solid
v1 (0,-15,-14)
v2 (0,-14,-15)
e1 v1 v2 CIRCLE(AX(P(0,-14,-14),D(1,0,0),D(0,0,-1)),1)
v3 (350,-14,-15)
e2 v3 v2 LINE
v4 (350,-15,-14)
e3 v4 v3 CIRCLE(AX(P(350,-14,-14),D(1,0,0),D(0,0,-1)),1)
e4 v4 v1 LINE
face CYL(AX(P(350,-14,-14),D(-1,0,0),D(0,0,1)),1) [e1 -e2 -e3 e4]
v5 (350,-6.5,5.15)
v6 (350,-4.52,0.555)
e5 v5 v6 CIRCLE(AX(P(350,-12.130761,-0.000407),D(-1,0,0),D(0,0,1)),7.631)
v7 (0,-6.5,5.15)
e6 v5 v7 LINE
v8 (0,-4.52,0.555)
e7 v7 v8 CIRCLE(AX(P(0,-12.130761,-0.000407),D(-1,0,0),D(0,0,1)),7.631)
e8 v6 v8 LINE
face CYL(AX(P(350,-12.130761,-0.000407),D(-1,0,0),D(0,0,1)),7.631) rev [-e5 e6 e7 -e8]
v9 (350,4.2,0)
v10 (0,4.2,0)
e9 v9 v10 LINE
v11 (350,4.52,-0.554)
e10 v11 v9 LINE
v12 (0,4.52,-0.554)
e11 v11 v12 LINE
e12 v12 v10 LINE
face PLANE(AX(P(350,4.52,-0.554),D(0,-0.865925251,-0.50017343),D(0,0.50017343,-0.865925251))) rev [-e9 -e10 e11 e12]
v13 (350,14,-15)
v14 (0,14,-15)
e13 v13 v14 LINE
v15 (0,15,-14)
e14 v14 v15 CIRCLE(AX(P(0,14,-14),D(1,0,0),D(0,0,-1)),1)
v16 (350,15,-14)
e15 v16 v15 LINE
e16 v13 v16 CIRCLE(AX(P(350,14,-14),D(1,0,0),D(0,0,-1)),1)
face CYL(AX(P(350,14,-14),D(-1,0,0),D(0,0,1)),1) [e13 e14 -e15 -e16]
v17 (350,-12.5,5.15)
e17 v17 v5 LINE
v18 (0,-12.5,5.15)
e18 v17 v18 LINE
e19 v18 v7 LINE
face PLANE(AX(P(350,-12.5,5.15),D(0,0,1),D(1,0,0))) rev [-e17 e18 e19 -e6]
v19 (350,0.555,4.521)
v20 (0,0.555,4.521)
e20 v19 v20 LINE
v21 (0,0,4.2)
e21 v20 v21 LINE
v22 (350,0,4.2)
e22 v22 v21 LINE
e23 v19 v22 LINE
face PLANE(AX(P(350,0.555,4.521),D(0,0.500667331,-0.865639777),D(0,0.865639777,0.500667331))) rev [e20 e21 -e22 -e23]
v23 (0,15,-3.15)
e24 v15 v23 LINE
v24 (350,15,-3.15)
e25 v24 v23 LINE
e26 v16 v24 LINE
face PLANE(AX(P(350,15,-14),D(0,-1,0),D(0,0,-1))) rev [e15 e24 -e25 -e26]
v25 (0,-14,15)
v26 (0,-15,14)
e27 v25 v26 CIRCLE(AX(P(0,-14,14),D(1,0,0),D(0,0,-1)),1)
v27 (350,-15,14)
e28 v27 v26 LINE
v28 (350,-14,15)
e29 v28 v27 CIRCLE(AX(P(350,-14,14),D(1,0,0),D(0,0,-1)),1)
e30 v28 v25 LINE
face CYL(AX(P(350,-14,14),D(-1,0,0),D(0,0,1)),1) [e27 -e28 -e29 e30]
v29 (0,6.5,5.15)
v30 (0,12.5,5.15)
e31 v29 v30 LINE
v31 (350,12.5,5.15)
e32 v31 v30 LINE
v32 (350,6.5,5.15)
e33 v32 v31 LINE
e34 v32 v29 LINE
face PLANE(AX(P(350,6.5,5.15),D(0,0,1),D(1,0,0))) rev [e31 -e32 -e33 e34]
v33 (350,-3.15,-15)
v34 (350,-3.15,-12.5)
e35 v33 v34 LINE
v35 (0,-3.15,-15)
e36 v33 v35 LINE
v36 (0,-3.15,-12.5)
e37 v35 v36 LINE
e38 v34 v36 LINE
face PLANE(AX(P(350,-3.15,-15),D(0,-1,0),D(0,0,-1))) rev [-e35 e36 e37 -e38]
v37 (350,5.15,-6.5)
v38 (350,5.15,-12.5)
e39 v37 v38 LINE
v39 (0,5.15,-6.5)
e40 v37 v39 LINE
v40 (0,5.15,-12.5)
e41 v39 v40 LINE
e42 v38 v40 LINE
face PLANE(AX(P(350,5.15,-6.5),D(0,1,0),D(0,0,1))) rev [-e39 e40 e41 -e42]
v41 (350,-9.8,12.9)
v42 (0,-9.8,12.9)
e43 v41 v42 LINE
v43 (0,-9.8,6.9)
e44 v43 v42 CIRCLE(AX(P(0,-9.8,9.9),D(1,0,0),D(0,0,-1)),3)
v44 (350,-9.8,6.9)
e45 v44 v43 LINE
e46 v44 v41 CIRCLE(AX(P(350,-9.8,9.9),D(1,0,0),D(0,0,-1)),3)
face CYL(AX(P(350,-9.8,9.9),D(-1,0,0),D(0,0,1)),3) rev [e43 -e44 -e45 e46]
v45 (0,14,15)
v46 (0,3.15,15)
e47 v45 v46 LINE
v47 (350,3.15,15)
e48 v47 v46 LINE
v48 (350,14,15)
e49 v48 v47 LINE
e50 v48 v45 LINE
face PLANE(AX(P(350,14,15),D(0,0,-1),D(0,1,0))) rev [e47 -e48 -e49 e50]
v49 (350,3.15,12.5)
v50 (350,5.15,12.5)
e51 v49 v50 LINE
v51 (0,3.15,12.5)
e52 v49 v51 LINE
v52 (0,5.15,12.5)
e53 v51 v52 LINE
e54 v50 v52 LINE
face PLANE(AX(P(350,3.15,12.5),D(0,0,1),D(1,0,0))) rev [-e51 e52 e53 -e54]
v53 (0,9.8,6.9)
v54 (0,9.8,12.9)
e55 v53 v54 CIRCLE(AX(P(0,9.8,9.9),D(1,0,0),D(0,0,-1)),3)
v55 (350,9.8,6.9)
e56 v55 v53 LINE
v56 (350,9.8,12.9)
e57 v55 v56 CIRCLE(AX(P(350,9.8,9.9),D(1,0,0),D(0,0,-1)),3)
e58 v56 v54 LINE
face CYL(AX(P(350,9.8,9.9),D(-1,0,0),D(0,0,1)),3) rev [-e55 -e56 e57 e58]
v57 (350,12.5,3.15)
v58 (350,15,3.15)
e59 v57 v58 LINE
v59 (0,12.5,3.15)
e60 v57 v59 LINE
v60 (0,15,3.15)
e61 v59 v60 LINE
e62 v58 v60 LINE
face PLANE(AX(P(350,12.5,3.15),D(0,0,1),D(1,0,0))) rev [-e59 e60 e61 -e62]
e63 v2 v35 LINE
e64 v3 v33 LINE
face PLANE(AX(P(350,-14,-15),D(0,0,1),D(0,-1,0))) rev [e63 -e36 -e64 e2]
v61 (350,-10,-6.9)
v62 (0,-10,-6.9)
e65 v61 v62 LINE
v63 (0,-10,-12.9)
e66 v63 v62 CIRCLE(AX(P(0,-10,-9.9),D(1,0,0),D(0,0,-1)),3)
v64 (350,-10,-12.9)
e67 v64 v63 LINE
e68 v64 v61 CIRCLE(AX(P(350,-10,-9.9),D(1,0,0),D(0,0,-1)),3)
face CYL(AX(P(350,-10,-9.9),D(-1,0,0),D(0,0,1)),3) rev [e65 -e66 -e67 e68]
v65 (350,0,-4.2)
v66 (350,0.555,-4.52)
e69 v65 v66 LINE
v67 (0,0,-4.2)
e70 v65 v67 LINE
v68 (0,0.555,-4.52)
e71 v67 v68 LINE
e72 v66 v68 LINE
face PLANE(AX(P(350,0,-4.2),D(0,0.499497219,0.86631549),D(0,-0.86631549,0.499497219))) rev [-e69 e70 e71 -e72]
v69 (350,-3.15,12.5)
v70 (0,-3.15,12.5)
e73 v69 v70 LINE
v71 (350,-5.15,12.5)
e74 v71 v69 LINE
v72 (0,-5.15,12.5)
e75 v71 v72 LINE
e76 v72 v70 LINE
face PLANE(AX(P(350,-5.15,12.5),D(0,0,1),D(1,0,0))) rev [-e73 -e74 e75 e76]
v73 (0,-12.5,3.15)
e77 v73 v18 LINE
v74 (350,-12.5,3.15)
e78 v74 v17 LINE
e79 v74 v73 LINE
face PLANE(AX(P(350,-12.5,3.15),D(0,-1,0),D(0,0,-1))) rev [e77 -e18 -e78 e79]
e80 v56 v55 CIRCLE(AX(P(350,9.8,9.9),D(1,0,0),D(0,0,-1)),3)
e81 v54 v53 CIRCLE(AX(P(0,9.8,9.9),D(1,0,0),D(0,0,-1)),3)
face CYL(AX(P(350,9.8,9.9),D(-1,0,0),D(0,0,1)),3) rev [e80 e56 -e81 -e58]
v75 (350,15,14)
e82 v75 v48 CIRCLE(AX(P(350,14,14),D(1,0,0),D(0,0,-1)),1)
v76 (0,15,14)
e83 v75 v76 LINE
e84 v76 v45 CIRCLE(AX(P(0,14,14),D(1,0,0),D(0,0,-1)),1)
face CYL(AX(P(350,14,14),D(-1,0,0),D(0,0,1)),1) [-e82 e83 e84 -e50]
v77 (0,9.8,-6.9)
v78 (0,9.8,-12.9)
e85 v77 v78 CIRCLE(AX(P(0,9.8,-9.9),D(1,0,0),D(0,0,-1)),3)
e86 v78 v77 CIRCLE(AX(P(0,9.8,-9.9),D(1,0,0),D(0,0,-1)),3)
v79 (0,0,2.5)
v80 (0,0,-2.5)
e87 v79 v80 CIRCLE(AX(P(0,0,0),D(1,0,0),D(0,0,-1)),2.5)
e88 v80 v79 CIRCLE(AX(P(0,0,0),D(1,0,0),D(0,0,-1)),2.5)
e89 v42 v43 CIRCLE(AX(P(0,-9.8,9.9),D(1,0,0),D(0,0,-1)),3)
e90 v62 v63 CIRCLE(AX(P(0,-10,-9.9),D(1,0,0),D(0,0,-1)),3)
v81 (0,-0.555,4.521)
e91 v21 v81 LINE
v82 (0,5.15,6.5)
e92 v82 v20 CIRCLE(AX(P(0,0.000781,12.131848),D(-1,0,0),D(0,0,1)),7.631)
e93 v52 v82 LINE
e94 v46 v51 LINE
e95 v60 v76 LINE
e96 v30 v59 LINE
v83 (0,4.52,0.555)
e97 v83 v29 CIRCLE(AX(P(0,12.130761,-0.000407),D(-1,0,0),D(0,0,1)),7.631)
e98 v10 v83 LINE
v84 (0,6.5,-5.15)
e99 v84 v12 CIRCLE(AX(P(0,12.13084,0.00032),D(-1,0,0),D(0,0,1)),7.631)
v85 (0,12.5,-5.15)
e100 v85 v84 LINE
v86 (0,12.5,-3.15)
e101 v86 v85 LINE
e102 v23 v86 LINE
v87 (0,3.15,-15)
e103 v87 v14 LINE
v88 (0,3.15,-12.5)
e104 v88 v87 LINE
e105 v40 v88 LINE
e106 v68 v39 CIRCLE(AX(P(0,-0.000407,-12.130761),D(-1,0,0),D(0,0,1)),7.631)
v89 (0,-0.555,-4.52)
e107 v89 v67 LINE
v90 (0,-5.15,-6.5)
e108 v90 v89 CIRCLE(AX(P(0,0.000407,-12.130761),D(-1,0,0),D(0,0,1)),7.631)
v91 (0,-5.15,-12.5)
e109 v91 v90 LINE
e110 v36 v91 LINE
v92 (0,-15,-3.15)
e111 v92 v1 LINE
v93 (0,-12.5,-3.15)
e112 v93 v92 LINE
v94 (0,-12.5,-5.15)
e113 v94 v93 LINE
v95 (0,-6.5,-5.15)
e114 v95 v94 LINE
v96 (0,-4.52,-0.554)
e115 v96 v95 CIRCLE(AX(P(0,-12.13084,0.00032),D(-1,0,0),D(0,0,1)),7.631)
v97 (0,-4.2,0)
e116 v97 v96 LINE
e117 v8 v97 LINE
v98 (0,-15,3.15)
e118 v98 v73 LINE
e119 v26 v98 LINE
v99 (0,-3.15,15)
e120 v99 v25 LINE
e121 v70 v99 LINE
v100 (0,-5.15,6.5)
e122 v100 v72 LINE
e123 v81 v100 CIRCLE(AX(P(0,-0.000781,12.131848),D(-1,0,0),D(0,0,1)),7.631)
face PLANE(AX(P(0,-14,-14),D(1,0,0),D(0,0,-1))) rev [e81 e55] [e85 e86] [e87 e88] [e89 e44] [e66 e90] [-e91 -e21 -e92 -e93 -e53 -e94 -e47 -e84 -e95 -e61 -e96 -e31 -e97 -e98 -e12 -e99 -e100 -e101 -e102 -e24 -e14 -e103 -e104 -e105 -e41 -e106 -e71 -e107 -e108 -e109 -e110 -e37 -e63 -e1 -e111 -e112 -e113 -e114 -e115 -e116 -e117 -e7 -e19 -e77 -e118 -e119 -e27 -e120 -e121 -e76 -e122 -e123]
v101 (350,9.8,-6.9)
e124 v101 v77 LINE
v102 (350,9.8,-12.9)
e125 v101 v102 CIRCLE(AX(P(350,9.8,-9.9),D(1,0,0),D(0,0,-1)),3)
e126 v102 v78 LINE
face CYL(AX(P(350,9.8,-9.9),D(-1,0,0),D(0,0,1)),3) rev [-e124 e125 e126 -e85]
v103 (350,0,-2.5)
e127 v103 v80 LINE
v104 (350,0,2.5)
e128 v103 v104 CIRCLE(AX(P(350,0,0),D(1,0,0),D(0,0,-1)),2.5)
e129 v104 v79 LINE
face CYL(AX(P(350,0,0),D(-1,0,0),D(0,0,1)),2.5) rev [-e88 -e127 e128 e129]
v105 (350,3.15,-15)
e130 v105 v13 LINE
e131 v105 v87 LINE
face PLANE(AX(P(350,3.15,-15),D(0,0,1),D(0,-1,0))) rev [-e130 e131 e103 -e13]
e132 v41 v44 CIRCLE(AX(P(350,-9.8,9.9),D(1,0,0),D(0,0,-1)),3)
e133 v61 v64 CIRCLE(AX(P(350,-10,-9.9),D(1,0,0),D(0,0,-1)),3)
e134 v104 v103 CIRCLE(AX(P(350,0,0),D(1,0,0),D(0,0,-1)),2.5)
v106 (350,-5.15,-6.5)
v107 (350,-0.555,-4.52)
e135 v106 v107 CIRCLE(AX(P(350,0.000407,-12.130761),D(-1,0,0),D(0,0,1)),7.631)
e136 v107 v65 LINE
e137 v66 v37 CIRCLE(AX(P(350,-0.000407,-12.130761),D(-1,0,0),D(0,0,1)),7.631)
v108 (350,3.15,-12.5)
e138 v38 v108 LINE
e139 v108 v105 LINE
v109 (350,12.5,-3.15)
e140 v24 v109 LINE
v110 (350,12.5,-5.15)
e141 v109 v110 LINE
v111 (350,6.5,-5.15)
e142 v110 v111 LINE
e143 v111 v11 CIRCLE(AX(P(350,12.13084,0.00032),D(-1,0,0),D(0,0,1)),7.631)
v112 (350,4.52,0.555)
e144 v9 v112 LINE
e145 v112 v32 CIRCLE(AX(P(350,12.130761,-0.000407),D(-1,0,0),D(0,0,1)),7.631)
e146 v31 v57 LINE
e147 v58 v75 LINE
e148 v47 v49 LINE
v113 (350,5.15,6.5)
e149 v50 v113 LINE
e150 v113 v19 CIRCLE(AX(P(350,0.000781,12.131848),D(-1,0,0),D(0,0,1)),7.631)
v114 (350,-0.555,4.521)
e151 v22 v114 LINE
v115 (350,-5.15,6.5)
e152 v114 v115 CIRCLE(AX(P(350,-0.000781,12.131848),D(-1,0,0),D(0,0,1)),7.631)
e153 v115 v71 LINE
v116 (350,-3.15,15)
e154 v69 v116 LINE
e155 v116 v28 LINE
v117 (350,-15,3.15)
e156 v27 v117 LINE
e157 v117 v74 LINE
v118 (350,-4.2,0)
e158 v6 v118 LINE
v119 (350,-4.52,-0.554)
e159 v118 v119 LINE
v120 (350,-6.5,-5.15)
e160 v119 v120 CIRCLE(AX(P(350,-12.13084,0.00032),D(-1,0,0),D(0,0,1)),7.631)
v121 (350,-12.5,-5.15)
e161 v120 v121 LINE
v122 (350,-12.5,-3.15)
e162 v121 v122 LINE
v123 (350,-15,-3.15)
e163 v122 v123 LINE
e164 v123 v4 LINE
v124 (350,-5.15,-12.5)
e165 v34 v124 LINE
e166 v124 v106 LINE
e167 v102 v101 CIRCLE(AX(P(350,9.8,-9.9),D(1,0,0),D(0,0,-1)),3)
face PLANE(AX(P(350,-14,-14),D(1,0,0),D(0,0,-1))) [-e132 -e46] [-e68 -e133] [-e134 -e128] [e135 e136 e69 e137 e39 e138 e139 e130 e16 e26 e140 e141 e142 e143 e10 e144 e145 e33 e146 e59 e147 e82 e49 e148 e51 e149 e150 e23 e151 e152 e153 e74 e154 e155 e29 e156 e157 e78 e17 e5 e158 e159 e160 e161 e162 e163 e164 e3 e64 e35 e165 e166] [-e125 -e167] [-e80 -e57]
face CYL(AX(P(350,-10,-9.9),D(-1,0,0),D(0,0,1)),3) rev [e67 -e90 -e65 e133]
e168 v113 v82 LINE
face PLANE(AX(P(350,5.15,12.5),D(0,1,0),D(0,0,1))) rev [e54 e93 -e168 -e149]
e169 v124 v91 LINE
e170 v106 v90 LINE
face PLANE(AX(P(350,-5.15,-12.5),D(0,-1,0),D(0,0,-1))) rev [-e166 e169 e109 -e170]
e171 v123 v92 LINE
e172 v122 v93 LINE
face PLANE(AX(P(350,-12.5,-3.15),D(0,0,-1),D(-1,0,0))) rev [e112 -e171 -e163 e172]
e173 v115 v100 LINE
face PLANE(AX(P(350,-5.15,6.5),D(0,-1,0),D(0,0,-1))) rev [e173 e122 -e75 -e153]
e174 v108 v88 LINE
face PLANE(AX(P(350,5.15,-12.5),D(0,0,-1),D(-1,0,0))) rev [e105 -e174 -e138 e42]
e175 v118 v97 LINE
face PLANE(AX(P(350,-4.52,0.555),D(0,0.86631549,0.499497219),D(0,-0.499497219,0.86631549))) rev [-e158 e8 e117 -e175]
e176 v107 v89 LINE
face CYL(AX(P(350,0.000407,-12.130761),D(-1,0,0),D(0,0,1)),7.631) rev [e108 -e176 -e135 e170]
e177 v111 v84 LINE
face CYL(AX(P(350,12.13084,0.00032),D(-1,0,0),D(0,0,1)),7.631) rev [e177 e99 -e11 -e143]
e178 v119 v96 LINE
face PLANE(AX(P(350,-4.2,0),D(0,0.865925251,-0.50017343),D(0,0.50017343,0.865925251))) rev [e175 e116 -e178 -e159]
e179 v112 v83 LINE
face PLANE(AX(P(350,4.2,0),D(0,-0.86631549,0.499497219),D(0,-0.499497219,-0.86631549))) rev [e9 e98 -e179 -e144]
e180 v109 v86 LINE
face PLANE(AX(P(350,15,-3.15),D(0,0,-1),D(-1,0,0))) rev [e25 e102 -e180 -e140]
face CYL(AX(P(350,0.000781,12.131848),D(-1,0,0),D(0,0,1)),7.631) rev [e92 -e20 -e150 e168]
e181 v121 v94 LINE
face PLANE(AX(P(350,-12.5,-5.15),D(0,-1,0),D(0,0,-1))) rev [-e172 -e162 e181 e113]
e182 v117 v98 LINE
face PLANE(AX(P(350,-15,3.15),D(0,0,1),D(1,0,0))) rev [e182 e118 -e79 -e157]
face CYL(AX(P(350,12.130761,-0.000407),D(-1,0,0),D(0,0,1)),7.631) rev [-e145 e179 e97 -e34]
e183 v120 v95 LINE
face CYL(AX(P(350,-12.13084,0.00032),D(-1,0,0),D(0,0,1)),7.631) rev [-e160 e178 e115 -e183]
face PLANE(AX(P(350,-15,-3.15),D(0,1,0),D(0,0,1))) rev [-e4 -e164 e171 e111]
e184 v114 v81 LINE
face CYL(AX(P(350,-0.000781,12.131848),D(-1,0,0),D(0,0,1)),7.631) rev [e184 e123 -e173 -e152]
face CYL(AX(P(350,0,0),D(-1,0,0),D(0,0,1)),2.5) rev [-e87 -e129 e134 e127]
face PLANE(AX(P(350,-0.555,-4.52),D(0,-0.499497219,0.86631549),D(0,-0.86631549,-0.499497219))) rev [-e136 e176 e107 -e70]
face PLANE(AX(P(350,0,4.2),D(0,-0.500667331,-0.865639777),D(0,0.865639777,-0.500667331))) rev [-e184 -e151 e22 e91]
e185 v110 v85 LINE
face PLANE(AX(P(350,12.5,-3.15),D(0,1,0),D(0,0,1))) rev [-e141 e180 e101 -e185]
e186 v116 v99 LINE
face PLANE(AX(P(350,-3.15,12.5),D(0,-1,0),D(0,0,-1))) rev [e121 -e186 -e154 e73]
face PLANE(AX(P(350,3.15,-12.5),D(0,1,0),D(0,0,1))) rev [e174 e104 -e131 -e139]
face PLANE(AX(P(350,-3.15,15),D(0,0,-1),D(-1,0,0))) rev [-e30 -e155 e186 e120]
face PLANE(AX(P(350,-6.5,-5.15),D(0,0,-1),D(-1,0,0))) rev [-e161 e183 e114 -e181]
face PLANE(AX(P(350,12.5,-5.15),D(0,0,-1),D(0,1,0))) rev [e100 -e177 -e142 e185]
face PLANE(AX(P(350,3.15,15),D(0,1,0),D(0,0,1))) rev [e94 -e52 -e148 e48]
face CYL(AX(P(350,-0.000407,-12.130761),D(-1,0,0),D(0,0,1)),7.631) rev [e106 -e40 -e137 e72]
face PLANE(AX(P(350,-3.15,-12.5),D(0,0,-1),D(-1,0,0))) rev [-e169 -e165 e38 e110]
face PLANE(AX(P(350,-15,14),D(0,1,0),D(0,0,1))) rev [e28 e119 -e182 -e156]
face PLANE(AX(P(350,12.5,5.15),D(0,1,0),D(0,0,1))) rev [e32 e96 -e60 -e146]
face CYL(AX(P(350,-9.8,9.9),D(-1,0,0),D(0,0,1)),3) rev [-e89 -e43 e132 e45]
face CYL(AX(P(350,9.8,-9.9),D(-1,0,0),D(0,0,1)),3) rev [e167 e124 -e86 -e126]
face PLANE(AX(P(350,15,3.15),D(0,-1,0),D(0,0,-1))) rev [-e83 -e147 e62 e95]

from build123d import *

# Parameters (mm, degrees)
SKETCH_11_R         = 3
SKETCH_11_R_2       = 2.5
F_0_GY_3030_1_DEPTH = 350


with BuildPart() as part:
    # 草图11 → 0国耀铝型材 GY-3030国标铝型材(1) (new body)
    with BuildSketch(Plane.YZ):
        with BuildLine():
            Line((-14, -15), (-3.15, -15))
            Line((-3.15, -15), (-3.15, -12.5))
            Line((-3.15, -12.5), (-5.15, -12.5))
            Line((-5.15, -12.5), (-5.15, -6.5))
            ThreePointArc((-5.15, -6.5), (-3.019390742, -5.122695475), (-0.555, -4.52))
            Line((-0.555, -4.52), (0, -4.2))
            Line((0, -4.2), (0.555, -4.52))
            ThreePointArc((0.555, -4.52), (3.019390742, -5.122695475), (5.15, -6.5))
            Line((5.15, -6.5), (5.15, -12.5))
            Line((5.15, -12.5), (3.15, -12.5))
            Line((3.15, -12.5), (3.15, -15))
            Line((3.15, -15), (14, -15))
            ThreePointArc((14, -15), (14.707106781, -14.707106781), (15, -14))
            Line((15, -14), (15, -3.15))
            Line((15, -3.15), (12.5, -3.15))
            Line((12.5, -3.15), (12.5, -5.15))
            Line((12.5, -5.15), (6.5, -5.15))
            ThreePointArc((6.5, -5.15), (5.12253592, -3.018923167), (4.52, -0.554))
            Line((4.52, -0.554), (4.2, 0))
            Line((4.2, 0), (4.52, 0.555))
            ThreePointArc((4.52, 0.555), (5.122695475, 3.019390742), (6.5, 5.15))
            Line((6.5, 5.15), (12.5, 5.15))
            Line((12.5, 5.15), (12.5, 3.15))
            Line((12.5, 3.15), (15, 3.15))
            Line((15, 3.15), (15, 14))
            ThreePointArc((15, 14), (14.707106781, 14.707106781), (14, 15))
            Line((14, 15), (3.15, 15))
            Line((3.15, 15), (3.15, 12.5))
            Line((3.15, 12.5), (5.15, 12.5))
            Line((5.15, 12.5), (5.15, 6.5))
            ThreePointArc((5.15, 6.5), (3.019292492, 5.123227892), (0.555, 4.521))
            Line((0.555, 4.521), (0, 4.2))
            Line((0, 4.2), (-0.555, 4.521))
            ThreePointArc((-0.555, 4.521), (-3.019292492, 5.123227892), (-5.15, 6.5))
            Line((-5.15, 6.5), (-5.15, 12.5))
            Line((-5.15, 12.5), (-3.15, 12.5))
            Line((-3.15, 12.5), (-3.15, 15))
            Line((-3.15, 15), (-14, 15))
            ThreePointArc((-14, 15), (-14.707106781, 14.707106781), (-15, 14))
            Line((-15, 14), (-15, 3.15))
            Line((-15, 3.15), (-12.5, 3.15))
            Line((-12.5, 3.15), (-12.5, 5.15))
            Line((-12.5, 5.15), (-6.5, 5.15))
            ThreePointArc((-6.5, 5.15), (-5.122695475, 3.019390742), (-4.52, 0.555))
            Line((-4.52, 0.555), (-4.2, 0))
            Line((-4.2, 0), (-4.52, -0.554))
            ThreePointArc((-4.52, -0.554), (-5.12253592, -3.018923167), (-6.5, -5.15))
            Line((-6.5, -5.15), (-12.5, -5.15))
            Line((-12.5, -5.15), (-12.5, -3.15))
            Line((-12.5, -3.15), (-15, -3.15))
            Line((-15, -3.15), (-15, -14))
            ThreePointArc((-15, -14), (-14.707106781, -14.707106781), (-14, -15))
        make_face()
        with Locations((9.8, 9.9)):
            Circle(SKETCH_11_R, mode=Mode.SUBTRACT)
        with Locations((9.8, -9.9)):
            Circle(SKETCH_11_R, mode=Mode.SUBTRACT)
        Circle(SKETCH_11_R_2, mode=Mode.SUBTRACT)
        with Locations((-9.8, 9.9)):
            Circle(SKETCH_11_R, mode=Mode.SUBTRACT)
        with Locations((-10, -9.9)):
            Circle(SKETCH_11_R, mode=Mode.SUBTRACT)
    extrude(amount=F_0_GY_3030_1_DEPTH)


solid = part.part
